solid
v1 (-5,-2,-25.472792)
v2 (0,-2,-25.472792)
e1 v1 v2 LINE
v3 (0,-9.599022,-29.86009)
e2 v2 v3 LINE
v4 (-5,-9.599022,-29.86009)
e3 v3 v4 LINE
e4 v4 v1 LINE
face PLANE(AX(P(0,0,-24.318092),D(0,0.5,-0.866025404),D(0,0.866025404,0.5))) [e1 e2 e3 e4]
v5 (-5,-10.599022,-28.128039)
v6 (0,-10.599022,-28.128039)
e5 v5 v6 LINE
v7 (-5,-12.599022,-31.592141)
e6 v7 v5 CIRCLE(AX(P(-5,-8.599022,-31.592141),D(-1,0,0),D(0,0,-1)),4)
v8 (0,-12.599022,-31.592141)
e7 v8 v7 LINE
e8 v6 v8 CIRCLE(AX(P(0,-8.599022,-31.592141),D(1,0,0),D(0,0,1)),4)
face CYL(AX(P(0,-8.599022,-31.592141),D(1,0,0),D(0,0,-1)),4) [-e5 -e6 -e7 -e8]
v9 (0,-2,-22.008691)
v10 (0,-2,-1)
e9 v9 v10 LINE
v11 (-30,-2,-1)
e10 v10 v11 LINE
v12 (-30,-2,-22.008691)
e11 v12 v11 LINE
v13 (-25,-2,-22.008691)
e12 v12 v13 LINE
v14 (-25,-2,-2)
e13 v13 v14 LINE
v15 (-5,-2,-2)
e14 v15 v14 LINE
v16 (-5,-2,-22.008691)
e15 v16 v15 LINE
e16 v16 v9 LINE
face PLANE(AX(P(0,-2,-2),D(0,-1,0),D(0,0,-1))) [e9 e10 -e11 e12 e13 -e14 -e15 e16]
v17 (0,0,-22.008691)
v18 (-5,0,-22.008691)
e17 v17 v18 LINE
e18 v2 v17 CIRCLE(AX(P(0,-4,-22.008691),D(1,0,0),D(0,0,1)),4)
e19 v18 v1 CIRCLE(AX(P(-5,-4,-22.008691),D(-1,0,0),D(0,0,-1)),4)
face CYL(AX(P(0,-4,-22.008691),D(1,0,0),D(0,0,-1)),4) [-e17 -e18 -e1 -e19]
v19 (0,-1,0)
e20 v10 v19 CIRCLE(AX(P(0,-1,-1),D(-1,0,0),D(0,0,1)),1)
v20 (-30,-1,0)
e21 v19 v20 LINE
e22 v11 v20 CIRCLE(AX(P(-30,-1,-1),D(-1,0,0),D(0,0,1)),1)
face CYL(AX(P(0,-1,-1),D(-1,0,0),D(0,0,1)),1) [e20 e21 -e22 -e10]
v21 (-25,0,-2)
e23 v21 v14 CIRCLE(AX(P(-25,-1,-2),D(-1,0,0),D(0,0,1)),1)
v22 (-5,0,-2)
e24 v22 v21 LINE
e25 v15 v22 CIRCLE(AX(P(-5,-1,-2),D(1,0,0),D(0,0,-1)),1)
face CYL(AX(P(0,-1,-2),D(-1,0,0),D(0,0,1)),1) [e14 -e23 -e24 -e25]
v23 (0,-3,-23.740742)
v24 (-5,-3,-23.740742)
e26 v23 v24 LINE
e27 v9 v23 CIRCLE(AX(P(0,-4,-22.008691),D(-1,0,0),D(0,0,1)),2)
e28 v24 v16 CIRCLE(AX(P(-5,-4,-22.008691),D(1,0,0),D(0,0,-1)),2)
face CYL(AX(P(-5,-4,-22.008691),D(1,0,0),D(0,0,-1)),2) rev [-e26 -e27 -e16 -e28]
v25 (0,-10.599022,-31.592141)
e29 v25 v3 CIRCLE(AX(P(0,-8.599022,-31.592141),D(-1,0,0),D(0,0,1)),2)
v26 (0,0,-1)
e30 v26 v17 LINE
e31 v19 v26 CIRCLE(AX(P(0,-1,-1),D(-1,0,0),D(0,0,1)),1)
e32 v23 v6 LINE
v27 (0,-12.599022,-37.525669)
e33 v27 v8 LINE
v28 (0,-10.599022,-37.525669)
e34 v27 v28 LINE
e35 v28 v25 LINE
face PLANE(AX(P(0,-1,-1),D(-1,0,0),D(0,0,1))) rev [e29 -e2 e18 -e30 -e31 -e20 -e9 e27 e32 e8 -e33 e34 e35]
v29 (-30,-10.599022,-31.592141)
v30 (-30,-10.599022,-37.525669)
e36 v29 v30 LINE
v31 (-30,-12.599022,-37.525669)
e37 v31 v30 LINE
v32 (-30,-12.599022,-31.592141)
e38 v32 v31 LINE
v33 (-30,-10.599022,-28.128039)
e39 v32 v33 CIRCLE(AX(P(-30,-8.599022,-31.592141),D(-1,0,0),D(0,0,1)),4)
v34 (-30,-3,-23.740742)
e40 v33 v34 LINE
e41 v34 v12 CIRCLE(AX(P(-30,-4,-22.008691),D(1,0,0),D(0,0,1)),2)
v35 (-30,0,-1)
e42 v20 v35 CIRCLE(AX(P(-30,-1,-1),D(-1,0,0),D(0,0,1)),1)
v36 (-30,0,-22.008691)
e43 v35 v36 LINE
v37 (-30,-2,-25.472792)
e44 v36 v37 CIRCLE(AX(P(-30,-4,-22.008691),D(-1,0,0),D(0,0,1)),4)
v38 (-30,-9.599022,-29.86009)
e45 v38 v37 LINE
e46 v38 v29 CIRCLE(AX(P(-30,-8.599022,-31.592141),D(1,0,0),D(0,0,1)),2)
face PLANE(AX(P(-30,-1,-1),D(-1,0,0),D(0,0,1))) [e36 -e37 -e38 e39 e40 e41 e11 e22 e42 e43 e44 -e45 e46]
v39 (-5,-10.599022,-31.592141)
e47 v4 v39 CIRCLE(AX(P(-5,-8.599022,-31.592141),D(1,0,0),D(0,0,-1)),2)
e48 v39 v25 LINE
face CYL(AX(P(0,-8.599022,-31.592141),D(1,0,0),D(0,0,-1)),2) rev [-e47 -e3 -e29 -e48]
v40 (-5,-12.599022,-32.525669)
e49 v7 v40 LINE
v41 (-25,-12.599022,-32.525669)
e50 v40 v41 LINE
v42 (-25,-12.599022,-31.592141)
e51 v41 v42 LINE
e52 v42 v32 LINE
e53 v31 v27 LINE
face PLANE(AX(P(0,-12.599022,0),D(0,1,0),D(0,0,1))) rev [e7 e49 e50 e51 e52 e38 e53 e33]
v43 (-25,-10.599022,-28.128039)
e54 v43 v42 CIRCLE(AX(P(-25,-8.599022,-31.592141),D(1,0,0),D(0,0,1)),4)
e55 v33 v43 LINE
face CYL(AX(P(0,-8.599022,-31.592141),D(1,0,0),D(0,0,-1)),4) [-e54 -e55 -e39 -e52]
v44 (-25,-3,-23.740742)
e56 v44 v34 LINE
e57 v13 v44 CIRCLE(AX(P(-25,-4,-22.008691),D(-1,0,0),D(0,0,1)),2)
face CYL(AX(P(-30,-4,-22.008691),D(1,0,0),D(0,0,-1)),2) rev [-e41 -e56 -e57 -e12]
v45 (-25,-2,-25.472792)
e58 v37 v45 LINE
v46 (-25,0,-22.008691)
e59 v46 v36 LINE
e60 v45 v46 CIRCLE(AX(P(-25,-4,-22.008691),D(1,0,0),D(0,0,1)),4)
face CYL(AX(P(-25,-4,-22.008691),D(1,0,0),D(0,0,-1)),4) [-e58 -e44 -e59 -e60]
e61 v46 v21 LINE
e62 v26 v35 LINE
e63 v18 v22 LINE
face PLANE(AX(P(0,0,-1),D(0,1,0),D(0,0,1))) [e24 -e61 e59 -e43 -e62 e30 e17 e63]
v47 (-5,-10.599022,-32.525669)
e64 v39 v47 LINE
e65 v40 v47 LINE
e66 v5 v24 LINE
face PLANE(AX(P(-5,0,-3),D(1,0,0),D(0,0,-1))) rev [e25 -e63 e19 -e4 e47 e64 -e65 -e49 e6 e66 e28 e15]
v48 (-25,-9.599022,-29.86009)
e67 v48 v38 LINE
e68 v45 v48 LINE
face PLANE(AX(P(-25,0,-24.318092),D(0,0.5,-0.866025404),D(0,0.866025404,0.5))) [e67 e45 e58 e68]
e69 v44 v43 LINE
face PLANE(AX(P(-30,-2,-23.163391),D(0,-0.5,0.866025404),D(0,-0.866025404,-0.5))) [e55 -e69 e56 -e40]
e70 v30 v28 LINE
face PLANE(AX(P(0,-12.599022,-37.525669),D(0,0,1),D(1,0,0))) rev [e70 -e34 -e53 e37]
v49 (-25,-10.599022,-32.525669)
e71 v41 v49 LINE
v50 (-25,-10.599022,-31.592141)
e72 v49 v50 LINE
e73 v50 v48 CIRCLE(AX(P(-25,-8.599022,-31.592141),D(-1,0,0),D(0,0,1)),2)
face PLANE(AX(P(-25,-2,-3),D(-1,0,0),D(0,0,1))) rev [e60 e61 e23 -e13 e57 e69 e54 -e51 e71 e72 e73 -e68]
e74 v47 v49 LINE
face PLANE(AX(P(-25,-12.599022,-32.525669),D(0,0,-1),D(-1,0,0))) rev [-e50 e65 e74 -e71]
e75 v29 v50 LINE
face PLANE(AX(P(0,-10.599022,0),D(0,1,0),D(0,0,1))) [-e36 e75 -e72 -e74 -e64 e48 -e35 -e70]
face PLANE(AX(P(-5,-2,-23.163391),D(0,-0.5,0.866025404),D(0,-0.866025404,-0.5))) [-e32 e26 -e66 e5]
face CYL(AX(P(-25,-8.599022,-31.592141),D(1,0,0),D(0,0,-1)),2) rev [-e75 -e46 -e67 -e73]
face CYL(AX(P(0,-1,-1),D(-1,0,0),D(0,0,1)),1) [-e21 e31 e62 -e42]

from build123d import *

# Parameters (mm, degrees)
BOSS_EXTRUDE1_DEPTH = 30
CUT_EXTRUDE1_START  = -5
CUT_EXTRUDE1_DEPTH  = 5
BOSS_EXTRUDE2_DEPTH = 1
SKETCH4_W           = 5
SKETCH4_H           = 2
BOSS_EXTRUDE3_DEPTH = 20.16339138
SKETCH5_W           = 5
SKETCH5_H           = 10.599022434
BOSS_EXTRUDE4_DEPTH = 1.154700538
CUT_EXTRUDE2_DEPTH  = 5
BOSS_EXTRUDE5_DEPTH = 1
SKETCH8_W           = 5
SKETCH8_H           = 2
BOSS_EXTRUDE6_DEPTH = 20.16339138
SKETCH9_W           = 5
SKETCH9_H           = 10.599022434
BOSS_EXTRUDE7_DEPTH = 1.154700538
BOSS_EXTRUDE8_DEPTH = 2
DRAFT1_ANGLE        = 30
DRAFT2_ANGLE        = 30
FILLET1_R           = 2
FILLET2_R           = 4


with BuildPart() as part:
    # Sketch1 → Boss-Extrude1 (new body)
    with BuildSketch(Plane(origin=(-30, 0, 0), x_dir=(0, -1, 0), z_dir=(-1, 0, 0))):
        with BuildLine():
            Line((0, -1), (0, -2))
            ThreePointArc((0, -2), (1, -3), (2, -2))
            Line((2, -2), (2, -1))
            ThreePointArc((2, -1), (1, 0), (0, -1))
        make_face()
    extrude(amount=-BOSS_EXTRUDE1_DEPTH)

    # Sketch2 → Cut-Extrude1 (cut)
    with BuildSketch(Plane(origin=(0, 0, 0), x_dir=(0, 0, -1), z_dir=(1, 0, 0)).offset(CUT_EXTRUDE1_START)):
        with BuildLine():
            Line((2, 0), (2, -2))
            ThreePointArc((2, -2), (3, -1), (2, 0))
        make_face()
    extrude(amount=CUT_EXTRUDE1_DEPTH, mode=Mode.SUBTRACT)

    # Sketch3 → Boss-Extrude2 (add)
    with BuildSketch(Plane(origin=(0, 0, -2), x_dir=(-1, 0, 0), z_dir=(0, 0, -1))):
        Polygon((5, -2), (0, -2), (0, 0), (5, 0), (5, -1), align=None)
    extrude(amount=BOSS_EXTRUDE2_DEPTH)

    # Sketch4 → Boss-Extrude3 (add)
    with BuildSketch(Plane(origin=(0, 0, -3), x_dir=(-1, 0, 0), z_dir=(0, 0, -1))):
        with Locations((2.5, -1)):
            Rectangle(SKETCH4_W, SKETCH4_H)
    extrude(amount=BOSS_EXTRUDE3_DEPTH)

    # Sketch5 → Boss-Extrude4 (add)
    with BuildSketch(Plane(origin=(0, 0, -23.16339138), x_dir=(-1, 0, 0), z_dir=(0, 0, -1))):
        with Locations((2.5, -5.299511217)):
            Rectangle(SKETCH5_W, SKETCH5_H)
    extrude(amount=BOSS_EXTRUDE4_DEPTH)

    # Sketch6 → Cut-Extrude2 (cut)
    with BuildSketch(Plane.ZY.offset(30)):
        with BuildLine():
            Line((-2, -2), (-2, 0))
            ThreePointArc((-2, 0), (-3, -1), (-2, -2))
        make_face()
    extrude(amount=-CUT_EXTRUDE2_DEPTH, mode=Mode.SUBTRACT)

    # Sketch7 → Boss-Extrude5 (add)
    with BuildSketch(Plane(origin=(0, 0, -2), x_dir=(-1, 0, 0), z_dir=(0, 0, -1))):
        Polygon((30, -2), (25, -2), (25, -1), (25, 0), (30, 0), align=None)
    extrude(amount=BOSS_EXTRUDE5_DEPTH)

    # Sketch8 → Boss-Extrude6 (add)
    with BuildSketch(Plane(origin=(0, 0, -3), x_dir=(-1, 0, 0), z_dir=(0, 0, -1))):
        with Locations((27.5, -1)):
            Rectangle(SKETCH8_W, SKETCH8_H)
    extrude(amount=BOSS_EXTRUDE6_DEPTH)

    # Sketch9 → Boss-Extrude7 (add)
    with BuildSketch(Plane(origin=(0, 0, -23.16339138), x_dir=(-1, 0, 0), z_dir=(0, 0, -1))):
        with Locations((27.5, -5.299511217)):
            Rectangle(SKETCH9_W, SKETCH9_H)
    extrude(amount=BOSS_EXTRUDE7_DEPTH)

    # Sketch10 → Boss-Extrude8 (add)
    with BuildSketch(Plane.XZ.offset(10.599022434)):
        Polygon((0, -23.16339138), (0, -37.525669468), (-30, -37.525669468), (-30, -23.16339138), (-25, -23.16339138), (-25, -32.525669468), (-5, -32.525669468), (-5, -23.16339138), align=None)
    extrude(amount=BOSS_EXTRUDE8_DEPTH)

    # Draft1
    draft1_faces = [part.faces().sort_by_distance(p)[0] for p in [
        (-2.5, -5.299511217, -24.318091918),
        (-27.5, -5.299511217, -24.318091918),
    ]]
    draft(draft1_faces, Plane(origin=(0, 0, -1), x_dir=(0, 0, 1), z_dir=(0, 1, 0)), DRAFT1_ANGLE)

    # Draft2
    draft2_faces = [part.faces().sort_by_distance(p)[0] for p in [
        (-27.5, -7.299511217, -23.16339138),
        (-2.5, -7.299511217, -23.16339138),
    ]]
    draft(draft2_faces, Plane(origin=(0, -2, -2), x_dir=(0, 0, -1), z_dir=(0, -1, 0)), DRAFT2_ANGLE)

    # Fillet1
    fillet1_edges = [part.edges().sort_by_distance(p)[0] for p in [
        (-27.5, -10.599022434, -30.437440374),
        (-2.5, -2, -23.16339138),
        (-2.5, -10.599022434, -30.437440374),
        (-27.5, -2, -23.16339138),
    ]]
    fillet(fillet1_edges, radius=FILLET1_R)

    # Fillet2
    fillet2_edges = [part.edges().sort_by_distance(p)[0] for p in [
        (-27.5, 0, -24.318091918),
        (-2.5, -12.599022434, -29.282739835),
        (-27.5, -12.599022434, -29.282739835),
        (-2.5, 0, -24.318091918),
    ]]
    fillet(fillet2_edges, radius=FILLET2_R)


solid = part.part
